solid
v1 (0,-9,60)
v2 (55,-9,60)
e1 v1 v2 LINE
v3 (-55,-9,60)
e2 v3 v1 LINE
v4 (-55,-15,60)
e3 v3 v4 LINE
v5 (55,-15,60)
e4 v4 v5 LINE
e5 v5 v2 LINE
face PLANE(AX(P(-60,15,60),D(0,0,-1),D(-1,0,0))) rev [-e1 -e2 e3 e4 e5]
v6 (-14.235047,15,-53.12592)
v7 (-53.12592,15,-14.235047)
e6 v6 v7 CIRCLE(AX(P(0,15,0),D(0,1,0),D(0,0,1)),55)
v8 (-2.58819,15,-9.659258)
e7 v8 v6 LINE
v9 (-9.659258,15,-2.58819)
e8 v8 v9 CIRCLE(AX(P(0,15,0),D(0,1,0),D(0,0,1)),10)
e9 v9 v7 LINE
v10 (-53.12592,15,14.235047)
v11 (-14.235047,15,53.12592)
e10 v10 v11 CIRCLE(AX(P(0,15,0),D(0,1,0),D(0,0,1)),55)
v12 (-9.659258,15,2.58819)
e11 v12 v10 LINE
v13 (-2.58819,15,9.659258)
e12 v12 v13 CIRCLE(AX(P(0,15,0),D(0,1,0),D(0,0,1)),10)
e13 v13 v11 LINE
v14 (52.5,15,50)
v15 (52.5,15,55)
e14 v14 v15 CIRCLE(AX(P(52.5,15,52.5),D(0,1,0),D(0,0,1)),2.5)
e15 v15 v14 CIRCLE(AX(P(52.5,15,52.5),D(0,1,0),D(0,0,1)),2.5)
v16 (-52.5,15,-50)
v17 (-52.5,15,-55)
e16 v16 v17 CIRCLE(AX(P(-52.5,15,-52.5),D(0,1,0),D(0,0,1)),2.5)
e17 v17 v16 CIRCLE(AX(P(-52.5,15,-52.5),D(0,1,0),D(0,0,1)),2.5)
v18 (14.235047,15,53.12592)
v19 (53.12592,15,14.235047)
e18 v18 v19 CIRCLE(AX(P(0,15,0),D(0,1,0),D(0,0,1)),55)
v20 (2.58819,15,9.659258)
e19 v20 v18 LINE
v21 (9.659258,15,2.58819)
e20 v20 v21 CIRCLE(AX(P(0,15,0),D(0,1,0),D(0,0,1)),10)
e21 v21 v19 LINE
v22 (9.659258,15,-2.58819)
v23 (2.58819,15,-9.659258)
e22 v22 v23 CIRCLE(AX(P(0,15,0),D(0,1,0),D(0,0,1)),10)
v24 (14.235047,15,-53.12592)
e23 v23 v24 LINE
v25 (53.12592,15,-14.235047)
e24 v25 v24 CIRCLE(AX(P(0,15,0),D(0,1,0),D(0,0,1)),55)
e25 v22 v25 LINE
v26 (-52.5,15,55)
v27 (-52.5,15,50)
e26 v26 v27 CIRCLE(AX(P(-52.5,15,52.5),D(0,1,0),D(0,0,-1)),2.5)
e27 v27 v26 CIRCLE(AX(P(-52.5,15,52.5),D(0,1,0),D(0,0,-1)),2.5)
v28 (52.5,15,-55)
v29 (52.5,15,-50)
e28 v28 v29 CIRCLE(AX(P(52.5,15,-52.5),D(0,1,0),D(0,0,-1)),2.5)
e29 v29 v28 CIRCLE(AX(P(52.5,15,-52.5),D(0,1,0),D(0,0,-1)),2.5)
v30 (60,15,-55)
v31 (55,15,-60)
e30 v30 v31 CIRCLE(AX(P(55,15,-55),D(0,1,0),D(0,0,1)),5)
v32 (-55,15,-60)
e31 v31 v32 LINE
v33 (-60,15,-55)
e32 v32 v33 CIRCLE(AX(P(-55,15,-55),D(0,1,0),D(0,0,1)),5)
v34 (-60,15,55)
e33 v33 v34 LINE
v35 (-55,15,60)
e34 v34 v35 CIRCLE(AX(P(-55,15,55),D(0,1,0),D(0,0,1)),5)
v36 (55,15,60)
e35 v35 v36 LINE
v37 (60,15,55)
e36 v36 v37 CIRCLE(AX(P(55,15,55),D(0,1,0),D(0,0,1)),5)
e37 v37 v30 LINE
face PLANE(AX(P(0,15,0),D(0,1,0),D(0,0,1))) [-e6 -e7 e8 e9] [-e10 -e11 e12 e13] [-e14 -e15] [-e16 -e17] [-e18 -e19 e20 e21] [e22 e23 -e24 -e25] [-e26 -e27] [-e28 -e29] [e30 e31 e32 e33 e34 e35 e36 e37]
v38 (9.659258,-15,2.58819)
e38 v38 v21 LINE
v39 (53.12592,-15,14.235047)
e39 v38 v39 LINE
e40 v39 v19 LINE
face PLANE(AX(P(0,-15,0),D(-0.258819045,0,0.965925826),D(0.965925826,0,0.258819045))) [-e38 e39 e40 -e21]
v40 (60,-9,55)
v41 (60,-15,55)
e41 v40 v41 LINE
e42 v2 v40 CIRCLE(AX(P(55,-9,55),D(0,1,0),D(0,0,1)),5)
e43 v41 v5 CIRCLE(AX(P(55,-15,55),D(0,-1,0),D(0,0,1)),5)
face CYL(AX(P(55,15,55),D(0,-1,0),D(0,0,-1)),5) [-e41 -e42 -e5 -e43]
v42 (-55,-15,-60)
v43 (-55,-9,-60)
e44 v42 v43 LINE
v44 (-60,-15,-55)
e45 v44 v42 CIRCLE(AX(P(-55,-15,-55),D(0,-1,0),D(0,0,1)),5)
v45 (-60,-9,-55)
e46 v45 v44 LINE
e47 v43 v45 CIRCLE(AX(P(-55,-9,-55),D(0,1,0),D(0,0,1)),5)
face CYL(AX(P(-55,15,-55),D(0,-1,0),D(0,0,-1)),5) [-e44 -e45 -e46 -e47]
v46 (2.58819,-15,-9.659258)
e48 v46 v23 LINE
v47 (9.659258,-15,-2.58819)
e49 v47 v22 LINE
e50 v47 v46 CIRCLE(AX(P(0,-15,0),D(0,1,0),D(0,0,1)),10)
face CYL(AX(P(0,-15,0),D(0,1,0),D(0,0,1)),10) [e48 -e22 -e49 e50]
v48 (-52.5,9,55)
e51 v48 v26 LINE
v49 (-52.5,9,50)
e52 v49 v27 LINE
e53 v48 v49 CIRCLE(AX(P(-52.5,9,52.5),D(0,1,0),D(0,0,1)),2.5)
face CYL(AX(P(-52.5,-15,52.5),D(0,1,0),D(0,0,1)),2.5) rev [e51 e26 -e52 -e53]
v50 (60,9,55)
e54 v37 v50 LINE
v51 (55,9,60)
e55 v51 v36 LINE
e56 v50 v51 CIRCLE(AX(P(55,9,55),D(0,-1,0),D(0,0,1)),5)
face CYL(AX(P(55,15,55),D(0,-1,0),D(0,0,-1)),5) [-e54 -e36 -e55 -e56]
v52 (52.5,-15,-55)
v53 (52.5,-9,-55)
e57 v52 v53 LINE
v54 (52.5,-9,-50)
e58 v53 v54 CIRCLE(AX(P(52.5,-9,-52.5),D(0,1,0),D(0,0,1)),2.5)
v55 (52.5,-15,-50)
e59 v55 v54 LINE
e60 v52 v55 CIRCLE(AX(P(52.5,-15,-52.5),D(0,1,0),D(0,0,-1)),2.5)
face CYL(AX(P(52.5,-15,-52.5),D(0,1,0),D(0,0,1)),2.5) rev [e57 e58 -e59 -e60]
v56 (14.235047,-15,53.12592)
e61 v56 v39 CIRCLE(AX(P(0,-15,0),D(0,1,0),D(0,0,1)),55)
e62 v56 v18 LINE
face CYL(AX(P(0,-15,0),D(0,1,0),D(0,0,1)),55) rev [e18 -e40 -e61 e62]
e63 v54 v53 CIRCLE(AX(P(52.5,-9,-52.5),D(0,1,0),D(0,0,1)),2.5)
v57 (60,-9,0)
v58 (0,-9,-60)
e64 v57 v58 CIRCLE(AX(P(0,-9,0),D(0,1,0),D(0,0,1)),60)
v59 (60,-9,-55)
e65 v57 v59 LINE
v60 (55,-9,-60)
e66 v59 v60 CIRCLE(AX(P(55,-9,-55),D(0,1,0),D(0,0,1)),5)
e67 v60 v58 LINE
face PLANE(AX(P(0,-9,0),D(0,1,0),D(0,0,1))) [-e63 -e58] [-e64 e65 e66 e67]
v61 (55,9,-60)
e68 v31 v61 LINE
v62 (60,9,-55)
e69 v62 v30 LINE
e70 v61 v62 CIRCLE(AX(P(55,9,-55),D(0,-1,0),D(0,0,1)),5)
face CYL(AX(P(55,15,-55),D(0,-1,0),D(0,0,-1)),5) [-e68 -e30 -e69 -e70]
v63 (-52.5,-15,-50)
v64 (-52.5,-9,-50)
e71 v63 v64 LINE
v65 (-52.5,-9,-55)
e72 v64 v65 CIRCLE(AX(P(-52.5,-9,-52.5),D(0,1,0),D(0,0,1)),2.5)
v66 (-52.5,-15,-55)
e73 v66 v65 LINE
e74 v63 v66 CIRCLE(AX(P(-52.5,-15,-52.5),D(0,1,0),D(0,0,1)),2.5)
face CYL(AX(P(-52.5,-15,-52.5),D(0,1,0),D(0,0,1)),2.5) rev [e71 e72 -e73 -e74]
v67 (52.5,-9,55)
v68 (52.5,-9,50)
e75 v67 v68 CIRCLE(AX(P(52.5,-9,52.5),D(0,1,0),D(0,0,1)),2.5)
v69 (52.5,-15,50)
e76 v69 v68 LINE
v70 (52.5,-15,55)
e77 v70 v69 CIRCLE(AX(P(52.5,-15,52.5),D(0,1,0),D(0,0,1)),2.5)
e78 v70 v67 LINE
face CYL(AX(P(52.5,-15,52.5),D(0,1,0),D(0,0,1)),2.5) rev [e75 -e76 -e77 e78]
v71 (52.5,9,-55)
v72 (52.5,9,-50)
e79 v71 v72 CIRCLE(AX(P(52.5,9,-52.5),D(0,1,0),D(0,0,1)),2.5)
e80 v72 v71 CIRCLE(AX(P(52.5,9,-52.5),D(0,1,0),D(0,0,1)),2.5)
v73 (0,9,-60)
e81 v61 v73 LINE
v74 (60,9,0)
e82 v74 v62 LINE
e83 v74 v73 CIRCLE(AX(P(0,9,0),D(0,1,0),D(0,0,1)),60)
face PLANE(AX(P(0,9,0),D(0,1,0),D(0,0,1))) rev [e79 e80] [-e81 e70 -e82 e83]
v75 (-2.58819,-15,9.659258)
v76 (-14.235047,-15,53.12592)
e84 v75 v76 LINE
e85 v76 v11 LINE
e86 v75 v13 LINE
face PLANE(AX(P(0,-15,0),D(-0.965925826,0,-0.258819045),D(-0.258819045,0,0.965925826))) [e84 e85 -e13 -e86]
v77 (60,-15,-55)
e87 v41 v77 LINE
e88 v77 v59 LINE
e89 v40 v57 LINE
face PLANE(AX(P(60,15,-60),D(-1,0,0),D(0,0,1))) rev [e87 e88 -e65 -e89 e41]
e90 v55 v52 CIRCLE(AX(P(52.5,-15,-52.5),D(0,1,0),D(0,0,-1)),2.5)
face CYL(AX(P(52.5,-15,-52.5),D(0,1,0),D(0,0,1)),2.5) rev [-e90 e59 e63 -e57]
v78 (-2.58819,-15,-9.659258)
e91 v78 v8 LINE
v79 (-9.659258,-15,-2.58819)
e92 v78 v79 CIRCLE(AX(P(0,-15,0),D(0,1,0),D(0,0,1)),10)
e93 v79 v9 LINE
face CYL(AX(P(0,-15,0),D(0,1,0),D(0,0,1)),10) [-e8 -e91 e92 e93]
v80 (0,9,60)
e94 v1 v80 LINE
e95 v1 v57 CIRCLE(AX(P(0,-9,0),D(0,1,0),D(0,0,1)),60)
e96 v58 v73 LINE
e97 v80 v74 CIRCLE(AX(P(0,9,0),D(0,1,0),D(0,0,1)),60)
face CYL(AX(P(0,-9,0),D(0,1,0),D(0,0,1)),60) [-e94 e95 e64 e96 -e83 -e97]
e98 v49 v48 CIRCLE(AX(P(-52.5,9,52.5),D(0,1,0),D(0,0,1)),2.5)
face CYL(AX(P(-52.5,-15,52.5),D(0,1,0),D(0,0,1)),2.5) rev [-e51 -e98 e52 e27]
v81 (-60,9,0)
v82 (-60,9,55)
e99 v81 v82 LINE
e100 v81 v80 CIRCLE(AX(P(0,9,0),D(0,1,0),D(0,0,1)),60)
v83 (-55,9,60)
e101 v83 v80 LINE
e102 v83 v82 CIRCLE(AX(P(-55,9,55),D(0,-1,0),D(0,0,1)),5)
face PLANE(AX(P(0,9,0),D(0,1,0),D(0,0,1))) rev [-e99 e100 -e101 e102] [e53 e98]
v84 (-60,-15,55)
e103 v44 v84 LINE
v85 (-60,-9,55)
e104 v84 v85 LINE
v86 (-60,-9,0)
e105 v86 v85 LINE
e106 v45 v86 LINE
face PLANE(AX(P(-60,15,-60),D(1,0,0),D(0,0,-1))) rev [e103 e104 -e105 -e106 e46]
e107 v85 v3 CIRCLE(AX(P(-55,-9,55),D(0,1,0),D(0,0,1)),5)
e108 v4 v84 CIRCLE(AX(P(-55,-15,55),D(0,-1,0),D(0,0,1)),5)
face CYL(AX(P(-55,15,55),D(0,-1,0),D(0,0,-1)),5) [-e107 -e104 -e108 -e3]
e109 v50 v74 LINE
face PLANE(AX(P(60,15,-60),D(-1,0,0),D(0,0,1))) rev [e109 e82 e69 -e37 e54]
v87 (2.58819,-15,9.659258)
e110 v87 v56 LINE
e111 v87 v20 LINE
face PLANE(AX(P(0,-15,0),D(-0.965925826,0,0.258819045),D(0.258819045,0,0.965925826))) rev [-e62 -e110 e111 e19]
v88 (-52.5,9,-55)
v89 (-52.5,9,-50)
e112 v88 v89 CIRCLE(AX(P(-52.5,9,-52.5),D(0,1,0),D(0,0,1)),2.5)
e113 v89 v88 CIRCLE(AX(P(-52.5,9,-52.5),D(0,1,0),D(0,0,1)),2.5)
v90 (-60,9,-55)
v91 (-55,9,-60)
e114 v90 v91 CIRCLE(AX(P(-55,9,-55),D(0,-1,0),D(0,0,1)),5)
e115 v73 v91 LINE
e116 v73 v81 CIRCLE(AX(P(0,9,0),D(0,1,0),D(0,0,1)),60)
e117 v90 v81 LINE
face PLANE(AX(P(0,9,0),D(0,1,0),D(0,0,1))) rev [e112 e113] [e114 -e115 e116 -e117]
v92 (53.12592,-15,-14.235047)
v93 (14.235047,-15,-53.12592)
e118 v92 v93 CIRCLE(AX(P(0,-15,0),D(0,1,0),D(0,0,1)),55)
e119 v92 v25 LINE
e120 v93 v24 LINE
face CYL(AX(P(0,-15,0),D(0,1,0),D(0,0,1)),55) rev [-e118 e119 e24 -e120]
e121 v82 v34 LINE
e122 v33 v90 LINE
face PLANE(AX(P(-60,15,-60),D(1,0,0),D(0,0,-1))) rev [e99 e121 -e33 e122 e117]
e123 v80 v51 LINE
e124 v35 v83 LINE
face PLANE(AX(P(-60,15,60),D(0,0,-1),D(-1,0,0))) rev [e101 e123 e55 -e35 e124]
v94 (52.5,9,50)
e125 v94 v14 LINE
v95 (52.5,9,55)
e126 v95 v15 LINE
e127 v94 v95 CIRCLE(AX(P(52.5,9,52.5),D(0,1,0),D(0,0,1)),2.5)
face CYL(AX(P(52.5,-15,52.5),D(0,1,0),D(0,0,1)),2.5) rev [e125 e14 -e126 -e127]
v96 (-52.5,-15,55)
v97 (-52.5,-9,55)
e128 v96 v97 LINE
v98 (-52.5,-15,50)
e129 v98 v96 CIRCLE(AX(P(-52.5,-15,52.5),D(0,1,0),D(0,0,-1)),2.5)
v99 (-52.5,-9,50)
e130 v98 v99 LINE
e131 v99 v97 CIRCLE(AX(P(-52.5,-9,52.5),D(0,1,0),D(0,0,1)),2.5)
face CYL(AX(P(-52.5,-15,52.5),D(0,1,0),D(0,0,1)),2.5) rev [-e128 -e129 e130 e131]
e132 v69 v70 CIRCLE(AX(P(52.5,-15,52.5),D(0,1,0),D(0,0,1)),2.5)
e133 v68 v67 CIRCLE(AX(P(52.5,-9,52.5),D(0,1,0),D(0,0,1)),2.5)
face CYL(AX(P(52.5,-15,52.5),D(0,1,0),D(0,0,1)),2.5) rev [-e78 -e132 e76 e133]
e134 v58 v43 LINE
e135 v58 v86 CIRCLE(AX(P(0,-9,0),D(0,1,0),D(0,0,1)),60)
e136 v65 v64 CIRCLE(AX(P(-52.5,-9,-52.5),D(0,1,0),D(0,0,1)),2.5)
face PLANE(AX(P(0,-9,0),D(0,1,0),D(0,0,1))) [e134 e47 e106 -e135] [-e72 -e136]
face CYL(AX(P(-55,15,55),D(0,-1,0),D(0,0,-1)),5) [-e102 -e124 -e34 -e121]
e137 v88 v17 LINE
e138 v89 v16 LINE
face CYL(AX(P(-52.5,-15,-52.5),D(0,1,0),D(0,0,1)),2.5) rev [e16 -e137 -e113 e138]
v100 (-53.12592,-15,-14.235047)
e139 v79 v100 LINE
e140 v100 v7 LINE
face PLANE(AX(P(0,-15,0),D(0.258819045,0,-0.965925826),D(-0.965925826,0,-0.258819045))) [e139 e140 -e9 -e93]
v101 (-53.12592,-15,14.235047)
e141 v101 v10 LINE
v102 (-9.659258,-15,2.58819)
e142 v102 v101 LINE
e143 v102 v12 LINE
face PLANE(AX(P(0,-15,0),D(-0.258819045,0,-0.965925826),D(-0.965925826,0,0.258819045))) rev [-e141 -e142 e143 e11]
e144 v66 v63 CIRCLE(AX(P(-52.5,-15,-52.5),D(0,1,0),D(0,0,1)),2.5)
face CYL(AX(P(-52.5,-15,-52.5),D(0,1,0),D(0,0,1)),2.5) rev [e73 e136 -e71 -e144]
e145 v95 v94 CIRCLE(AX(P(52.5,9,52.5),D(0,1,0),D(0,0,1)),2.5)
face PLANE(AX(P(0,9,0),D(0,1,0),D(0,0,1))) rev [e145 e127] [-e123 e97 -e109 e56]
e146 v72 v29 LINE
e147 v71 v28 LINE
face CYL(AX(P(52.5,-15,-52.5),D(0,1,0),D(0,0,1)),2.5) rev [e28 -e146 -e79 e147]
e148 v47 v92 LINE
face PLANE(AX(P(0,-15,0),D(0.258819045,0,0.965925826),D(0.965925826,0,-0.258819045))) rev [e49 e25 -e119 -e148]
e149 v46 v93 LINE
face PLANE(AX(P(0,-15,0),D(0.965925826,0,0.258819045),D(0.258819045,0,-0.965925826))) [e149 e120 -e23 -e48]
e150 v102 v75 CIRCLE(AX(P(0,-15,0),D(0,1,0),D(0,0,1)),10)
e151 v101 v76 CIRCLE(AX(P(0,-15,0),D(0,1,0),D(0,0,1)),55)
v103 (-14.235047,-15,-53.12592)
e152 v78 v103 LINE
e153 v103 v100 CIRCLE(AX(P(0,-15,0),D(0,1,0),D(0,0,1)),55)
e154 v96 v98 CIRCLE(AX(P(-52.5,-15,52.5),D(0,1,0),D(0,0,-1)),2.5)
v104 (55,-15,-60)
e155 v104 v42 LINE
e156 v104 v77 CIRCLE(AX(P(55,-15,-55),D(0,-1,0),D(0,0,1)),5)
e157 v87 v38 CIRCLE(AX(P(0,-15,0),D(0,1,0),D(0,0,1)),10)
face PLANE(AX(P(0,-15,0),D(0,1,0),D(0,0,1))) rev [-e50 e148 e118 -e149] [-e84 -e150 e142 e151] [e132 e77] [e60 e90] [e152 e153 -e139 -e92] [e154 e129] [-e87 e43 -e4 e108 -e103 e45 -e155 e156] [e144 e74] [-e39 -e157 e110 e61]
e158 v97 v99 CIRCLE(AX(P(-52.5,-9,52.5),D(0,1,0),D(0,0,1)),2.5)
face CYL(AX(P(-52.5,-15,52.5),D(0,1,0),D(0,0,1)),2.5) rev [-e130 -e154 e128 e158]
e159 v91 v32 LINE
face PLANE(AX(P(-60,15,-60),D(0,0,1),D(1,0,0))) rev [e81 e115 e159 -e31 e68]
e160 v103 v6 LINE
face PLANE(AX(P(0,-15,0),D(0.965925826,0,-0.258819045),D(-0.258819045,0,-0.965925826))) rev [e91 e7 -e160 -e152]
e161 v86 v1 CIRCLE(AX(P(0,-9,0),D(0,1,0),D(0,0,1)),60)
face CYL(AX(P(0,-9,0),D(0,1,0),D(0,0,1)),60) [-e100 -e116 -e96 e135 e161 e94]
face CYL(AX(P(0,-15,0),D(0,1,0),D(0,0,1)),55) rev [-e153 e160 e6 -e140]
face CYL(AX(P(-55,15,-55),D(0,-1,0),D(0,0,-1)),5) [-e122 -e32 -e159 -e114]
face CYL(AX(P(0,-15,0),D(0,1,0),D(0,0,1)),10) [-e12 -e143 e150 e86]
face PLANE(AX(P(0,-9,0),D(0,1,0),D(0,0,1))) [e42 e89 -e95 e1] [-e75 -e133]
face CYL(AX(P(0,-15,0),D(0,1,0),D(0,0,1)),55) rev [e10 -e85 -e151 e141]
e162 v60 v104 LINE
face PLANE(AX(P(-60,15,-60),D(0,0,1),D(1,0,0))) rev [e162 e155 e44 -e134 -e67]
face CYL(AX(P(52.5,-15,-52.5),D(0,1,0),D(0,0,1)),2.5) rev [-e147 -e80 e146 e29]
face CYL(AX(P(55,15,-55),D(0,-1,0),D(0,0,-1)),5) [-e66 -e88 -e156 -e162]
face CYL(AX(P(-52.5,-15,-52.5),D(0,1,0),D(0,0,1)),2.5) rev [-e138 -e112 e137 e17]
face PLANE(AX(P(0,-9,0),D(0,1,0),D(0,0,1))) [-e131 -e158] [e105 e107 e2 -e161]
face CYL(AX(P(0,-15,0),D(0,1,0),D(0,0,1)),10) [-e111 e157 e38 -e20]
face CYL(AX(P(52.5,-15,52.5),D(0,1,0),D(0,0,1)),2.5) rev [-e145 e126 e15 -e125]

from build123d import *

# Parameters (mm, degrees)
SKETCH_1_W          = 120
SKETCH_1_H          = 120
EXTRUDE_1_DEPTH     = 15
SKETCH_3_R          = 90.791455295
SKETCH_3_R_2        = 60
CUT_EXTRUDE_1_DEPTH = 9
SKETCH_4_R          = 2.5
CUT_EXTRUDE_3_DEPTH = 91
FILLET_1_R          = 5
CUT_EXTRUDE_4_DEPTH = 91


with BuildPart() as part:
    # 草图1 → 凸台-拉伸1 (new, symmetric)
    with BuildSketch(Plane(origin=(0, 0, 0), x_dir=(1, 0, 0), z_dir=(0, 1, 0))):
        Rectangle(SKETCH_1_W, SKETCH_1_H)
    extrude(amount=EXTRUDE_1_DEPTH, both=True)

    # 草图3 → 切除-拉伸1 (cut, symmetric)
    with BuildSketch(Plane(origin=(0, 0, 0), x_dir=(1, 0, 0), z_dir=(0, 1, 0))):
        Circle(SKETCH_3_R)
        with Locations(Location((0, 0, 0), (0, 0, 270))):
            Circle(SKETCH_3_R_2, mode=Mode.SUBTRACT)
    extrude(amount=CUT_EXTRUDE_1_DEPTH, both=True, mode=Mode.SUBTRACT)

    # 草图4 → 切除-拉伸3 (cut, through all)
    with BuildSketch(Plane(origin=(0, 15, 0), x_dir=(1, 0, 0), z_dir=(0, 1, 0))):
        with Locations(Location((-52.5, 52.5, 0), (0, 0, 270))):
            Circle(SKETCH_4_R)
        with Locations(Location((-52.5, -52.5, 0), (0, 0, 270))):
            Circle(SKETCH_4_R)
        with Locations(Location((52.5, -52.5, 0), (0, 0, 270))):
            Circle(SKETCH_4_R)
        with Locations(Location((52.5, 52.5, 0), (0, 0, 270))):
            Circle(SKETCH_4_R)
    extrude(amount=-CUT_EXTRUDE_3_DEPTH, mode=Mode.SUBTRACT)

    # 圆角1
    fillet_1_edges = [part.edges().sort_by_distance(p)[0] for p in [
        (60, -12, 60),
        (-60, -12, 60),
        (-60, -12, -60),
        (60, -12, -60),
        (60, 12, 60),
        (-60, 12, 60),
        (-60, 12, -60),
        (60, 12, -60),
    ]]
    fillet(fillet_1_edges, radius=FILLET_1_R)

    # 草图5 → 切除-拉伸4 (cut, through all)
    with BuildSketch(Plane(origin=(0, 15, 0), x_dir=(1, 0, 0), z_dir=(0, 1, 0))):
        with BuildLine():
            ThreePointArc((-9.659258263, 2.588190451), (-7.071067812, 7.071067812), (-2.588190451, 9.659258263))
            Line((-2.588190451, 9.659258263), (-14.235047481, 53.125920446))
            ThreePointArc((-14.235047481, 53.125920446), (-38.890872965, 38.890872965), (-53.125920446, 14.235047481))
            Line((-53.125920446, 14.235047481), (-9.659258263, 2.588190451))
        make_face()
        with BuildLine():
            Line((14.235047481, 53.125920446), (2.588190451, 9.659258263))
            ThreePointArc((2.588190451, 9.659258263), (7.071067812, 7.071067812), (9.659258263, 2.588190451))
            Line((9.659258263, 2.588190451), (53.125920446, 14.235047481))
            ThreePointArc((53.125920446, 14.235047481), (38.890872965, 38.890872965), (14.235047481, 53.125920446))
        make_face()
        with BuildLine():
            ThreePointArc((9.659258263, -2.588190451), (7.071067812, -7.071067812), (2.588190451, -9.659258263))
            Line((2.588190451, -9.659258263), (14.235047481, -53.125920446))
            ThreePointArc((14.235047481, -53.125920446), (38.890872965, -38.890872965), (53.125920446, -14.235047481))
            Line((53.125920446, -14.235047481), (9.659258263, -2.588190451))
        make_face()
        with BuildLine():
            Line((-14.235047481, -53.125920446), (-2.588190451, -9.659258263))
            ThreePointArc((-2.588190451, -9.659258263), (-7.071067812, -7.071067812), (-9.659258263, -2.588190451))
            Line((-9.659258263, -2.588190451), (-53.125920446, -14.235047481))
            ThreePointArc((-53.125920446, -14.235047481), (-38.890872965, -38.890872965), (-14.235047481, -53.125920446))
        make_face()
    extrude(amount=-CUT_EXTRUDE_4_DEPTH, mode=Mode.SUBTRACT)


solid = part.part
